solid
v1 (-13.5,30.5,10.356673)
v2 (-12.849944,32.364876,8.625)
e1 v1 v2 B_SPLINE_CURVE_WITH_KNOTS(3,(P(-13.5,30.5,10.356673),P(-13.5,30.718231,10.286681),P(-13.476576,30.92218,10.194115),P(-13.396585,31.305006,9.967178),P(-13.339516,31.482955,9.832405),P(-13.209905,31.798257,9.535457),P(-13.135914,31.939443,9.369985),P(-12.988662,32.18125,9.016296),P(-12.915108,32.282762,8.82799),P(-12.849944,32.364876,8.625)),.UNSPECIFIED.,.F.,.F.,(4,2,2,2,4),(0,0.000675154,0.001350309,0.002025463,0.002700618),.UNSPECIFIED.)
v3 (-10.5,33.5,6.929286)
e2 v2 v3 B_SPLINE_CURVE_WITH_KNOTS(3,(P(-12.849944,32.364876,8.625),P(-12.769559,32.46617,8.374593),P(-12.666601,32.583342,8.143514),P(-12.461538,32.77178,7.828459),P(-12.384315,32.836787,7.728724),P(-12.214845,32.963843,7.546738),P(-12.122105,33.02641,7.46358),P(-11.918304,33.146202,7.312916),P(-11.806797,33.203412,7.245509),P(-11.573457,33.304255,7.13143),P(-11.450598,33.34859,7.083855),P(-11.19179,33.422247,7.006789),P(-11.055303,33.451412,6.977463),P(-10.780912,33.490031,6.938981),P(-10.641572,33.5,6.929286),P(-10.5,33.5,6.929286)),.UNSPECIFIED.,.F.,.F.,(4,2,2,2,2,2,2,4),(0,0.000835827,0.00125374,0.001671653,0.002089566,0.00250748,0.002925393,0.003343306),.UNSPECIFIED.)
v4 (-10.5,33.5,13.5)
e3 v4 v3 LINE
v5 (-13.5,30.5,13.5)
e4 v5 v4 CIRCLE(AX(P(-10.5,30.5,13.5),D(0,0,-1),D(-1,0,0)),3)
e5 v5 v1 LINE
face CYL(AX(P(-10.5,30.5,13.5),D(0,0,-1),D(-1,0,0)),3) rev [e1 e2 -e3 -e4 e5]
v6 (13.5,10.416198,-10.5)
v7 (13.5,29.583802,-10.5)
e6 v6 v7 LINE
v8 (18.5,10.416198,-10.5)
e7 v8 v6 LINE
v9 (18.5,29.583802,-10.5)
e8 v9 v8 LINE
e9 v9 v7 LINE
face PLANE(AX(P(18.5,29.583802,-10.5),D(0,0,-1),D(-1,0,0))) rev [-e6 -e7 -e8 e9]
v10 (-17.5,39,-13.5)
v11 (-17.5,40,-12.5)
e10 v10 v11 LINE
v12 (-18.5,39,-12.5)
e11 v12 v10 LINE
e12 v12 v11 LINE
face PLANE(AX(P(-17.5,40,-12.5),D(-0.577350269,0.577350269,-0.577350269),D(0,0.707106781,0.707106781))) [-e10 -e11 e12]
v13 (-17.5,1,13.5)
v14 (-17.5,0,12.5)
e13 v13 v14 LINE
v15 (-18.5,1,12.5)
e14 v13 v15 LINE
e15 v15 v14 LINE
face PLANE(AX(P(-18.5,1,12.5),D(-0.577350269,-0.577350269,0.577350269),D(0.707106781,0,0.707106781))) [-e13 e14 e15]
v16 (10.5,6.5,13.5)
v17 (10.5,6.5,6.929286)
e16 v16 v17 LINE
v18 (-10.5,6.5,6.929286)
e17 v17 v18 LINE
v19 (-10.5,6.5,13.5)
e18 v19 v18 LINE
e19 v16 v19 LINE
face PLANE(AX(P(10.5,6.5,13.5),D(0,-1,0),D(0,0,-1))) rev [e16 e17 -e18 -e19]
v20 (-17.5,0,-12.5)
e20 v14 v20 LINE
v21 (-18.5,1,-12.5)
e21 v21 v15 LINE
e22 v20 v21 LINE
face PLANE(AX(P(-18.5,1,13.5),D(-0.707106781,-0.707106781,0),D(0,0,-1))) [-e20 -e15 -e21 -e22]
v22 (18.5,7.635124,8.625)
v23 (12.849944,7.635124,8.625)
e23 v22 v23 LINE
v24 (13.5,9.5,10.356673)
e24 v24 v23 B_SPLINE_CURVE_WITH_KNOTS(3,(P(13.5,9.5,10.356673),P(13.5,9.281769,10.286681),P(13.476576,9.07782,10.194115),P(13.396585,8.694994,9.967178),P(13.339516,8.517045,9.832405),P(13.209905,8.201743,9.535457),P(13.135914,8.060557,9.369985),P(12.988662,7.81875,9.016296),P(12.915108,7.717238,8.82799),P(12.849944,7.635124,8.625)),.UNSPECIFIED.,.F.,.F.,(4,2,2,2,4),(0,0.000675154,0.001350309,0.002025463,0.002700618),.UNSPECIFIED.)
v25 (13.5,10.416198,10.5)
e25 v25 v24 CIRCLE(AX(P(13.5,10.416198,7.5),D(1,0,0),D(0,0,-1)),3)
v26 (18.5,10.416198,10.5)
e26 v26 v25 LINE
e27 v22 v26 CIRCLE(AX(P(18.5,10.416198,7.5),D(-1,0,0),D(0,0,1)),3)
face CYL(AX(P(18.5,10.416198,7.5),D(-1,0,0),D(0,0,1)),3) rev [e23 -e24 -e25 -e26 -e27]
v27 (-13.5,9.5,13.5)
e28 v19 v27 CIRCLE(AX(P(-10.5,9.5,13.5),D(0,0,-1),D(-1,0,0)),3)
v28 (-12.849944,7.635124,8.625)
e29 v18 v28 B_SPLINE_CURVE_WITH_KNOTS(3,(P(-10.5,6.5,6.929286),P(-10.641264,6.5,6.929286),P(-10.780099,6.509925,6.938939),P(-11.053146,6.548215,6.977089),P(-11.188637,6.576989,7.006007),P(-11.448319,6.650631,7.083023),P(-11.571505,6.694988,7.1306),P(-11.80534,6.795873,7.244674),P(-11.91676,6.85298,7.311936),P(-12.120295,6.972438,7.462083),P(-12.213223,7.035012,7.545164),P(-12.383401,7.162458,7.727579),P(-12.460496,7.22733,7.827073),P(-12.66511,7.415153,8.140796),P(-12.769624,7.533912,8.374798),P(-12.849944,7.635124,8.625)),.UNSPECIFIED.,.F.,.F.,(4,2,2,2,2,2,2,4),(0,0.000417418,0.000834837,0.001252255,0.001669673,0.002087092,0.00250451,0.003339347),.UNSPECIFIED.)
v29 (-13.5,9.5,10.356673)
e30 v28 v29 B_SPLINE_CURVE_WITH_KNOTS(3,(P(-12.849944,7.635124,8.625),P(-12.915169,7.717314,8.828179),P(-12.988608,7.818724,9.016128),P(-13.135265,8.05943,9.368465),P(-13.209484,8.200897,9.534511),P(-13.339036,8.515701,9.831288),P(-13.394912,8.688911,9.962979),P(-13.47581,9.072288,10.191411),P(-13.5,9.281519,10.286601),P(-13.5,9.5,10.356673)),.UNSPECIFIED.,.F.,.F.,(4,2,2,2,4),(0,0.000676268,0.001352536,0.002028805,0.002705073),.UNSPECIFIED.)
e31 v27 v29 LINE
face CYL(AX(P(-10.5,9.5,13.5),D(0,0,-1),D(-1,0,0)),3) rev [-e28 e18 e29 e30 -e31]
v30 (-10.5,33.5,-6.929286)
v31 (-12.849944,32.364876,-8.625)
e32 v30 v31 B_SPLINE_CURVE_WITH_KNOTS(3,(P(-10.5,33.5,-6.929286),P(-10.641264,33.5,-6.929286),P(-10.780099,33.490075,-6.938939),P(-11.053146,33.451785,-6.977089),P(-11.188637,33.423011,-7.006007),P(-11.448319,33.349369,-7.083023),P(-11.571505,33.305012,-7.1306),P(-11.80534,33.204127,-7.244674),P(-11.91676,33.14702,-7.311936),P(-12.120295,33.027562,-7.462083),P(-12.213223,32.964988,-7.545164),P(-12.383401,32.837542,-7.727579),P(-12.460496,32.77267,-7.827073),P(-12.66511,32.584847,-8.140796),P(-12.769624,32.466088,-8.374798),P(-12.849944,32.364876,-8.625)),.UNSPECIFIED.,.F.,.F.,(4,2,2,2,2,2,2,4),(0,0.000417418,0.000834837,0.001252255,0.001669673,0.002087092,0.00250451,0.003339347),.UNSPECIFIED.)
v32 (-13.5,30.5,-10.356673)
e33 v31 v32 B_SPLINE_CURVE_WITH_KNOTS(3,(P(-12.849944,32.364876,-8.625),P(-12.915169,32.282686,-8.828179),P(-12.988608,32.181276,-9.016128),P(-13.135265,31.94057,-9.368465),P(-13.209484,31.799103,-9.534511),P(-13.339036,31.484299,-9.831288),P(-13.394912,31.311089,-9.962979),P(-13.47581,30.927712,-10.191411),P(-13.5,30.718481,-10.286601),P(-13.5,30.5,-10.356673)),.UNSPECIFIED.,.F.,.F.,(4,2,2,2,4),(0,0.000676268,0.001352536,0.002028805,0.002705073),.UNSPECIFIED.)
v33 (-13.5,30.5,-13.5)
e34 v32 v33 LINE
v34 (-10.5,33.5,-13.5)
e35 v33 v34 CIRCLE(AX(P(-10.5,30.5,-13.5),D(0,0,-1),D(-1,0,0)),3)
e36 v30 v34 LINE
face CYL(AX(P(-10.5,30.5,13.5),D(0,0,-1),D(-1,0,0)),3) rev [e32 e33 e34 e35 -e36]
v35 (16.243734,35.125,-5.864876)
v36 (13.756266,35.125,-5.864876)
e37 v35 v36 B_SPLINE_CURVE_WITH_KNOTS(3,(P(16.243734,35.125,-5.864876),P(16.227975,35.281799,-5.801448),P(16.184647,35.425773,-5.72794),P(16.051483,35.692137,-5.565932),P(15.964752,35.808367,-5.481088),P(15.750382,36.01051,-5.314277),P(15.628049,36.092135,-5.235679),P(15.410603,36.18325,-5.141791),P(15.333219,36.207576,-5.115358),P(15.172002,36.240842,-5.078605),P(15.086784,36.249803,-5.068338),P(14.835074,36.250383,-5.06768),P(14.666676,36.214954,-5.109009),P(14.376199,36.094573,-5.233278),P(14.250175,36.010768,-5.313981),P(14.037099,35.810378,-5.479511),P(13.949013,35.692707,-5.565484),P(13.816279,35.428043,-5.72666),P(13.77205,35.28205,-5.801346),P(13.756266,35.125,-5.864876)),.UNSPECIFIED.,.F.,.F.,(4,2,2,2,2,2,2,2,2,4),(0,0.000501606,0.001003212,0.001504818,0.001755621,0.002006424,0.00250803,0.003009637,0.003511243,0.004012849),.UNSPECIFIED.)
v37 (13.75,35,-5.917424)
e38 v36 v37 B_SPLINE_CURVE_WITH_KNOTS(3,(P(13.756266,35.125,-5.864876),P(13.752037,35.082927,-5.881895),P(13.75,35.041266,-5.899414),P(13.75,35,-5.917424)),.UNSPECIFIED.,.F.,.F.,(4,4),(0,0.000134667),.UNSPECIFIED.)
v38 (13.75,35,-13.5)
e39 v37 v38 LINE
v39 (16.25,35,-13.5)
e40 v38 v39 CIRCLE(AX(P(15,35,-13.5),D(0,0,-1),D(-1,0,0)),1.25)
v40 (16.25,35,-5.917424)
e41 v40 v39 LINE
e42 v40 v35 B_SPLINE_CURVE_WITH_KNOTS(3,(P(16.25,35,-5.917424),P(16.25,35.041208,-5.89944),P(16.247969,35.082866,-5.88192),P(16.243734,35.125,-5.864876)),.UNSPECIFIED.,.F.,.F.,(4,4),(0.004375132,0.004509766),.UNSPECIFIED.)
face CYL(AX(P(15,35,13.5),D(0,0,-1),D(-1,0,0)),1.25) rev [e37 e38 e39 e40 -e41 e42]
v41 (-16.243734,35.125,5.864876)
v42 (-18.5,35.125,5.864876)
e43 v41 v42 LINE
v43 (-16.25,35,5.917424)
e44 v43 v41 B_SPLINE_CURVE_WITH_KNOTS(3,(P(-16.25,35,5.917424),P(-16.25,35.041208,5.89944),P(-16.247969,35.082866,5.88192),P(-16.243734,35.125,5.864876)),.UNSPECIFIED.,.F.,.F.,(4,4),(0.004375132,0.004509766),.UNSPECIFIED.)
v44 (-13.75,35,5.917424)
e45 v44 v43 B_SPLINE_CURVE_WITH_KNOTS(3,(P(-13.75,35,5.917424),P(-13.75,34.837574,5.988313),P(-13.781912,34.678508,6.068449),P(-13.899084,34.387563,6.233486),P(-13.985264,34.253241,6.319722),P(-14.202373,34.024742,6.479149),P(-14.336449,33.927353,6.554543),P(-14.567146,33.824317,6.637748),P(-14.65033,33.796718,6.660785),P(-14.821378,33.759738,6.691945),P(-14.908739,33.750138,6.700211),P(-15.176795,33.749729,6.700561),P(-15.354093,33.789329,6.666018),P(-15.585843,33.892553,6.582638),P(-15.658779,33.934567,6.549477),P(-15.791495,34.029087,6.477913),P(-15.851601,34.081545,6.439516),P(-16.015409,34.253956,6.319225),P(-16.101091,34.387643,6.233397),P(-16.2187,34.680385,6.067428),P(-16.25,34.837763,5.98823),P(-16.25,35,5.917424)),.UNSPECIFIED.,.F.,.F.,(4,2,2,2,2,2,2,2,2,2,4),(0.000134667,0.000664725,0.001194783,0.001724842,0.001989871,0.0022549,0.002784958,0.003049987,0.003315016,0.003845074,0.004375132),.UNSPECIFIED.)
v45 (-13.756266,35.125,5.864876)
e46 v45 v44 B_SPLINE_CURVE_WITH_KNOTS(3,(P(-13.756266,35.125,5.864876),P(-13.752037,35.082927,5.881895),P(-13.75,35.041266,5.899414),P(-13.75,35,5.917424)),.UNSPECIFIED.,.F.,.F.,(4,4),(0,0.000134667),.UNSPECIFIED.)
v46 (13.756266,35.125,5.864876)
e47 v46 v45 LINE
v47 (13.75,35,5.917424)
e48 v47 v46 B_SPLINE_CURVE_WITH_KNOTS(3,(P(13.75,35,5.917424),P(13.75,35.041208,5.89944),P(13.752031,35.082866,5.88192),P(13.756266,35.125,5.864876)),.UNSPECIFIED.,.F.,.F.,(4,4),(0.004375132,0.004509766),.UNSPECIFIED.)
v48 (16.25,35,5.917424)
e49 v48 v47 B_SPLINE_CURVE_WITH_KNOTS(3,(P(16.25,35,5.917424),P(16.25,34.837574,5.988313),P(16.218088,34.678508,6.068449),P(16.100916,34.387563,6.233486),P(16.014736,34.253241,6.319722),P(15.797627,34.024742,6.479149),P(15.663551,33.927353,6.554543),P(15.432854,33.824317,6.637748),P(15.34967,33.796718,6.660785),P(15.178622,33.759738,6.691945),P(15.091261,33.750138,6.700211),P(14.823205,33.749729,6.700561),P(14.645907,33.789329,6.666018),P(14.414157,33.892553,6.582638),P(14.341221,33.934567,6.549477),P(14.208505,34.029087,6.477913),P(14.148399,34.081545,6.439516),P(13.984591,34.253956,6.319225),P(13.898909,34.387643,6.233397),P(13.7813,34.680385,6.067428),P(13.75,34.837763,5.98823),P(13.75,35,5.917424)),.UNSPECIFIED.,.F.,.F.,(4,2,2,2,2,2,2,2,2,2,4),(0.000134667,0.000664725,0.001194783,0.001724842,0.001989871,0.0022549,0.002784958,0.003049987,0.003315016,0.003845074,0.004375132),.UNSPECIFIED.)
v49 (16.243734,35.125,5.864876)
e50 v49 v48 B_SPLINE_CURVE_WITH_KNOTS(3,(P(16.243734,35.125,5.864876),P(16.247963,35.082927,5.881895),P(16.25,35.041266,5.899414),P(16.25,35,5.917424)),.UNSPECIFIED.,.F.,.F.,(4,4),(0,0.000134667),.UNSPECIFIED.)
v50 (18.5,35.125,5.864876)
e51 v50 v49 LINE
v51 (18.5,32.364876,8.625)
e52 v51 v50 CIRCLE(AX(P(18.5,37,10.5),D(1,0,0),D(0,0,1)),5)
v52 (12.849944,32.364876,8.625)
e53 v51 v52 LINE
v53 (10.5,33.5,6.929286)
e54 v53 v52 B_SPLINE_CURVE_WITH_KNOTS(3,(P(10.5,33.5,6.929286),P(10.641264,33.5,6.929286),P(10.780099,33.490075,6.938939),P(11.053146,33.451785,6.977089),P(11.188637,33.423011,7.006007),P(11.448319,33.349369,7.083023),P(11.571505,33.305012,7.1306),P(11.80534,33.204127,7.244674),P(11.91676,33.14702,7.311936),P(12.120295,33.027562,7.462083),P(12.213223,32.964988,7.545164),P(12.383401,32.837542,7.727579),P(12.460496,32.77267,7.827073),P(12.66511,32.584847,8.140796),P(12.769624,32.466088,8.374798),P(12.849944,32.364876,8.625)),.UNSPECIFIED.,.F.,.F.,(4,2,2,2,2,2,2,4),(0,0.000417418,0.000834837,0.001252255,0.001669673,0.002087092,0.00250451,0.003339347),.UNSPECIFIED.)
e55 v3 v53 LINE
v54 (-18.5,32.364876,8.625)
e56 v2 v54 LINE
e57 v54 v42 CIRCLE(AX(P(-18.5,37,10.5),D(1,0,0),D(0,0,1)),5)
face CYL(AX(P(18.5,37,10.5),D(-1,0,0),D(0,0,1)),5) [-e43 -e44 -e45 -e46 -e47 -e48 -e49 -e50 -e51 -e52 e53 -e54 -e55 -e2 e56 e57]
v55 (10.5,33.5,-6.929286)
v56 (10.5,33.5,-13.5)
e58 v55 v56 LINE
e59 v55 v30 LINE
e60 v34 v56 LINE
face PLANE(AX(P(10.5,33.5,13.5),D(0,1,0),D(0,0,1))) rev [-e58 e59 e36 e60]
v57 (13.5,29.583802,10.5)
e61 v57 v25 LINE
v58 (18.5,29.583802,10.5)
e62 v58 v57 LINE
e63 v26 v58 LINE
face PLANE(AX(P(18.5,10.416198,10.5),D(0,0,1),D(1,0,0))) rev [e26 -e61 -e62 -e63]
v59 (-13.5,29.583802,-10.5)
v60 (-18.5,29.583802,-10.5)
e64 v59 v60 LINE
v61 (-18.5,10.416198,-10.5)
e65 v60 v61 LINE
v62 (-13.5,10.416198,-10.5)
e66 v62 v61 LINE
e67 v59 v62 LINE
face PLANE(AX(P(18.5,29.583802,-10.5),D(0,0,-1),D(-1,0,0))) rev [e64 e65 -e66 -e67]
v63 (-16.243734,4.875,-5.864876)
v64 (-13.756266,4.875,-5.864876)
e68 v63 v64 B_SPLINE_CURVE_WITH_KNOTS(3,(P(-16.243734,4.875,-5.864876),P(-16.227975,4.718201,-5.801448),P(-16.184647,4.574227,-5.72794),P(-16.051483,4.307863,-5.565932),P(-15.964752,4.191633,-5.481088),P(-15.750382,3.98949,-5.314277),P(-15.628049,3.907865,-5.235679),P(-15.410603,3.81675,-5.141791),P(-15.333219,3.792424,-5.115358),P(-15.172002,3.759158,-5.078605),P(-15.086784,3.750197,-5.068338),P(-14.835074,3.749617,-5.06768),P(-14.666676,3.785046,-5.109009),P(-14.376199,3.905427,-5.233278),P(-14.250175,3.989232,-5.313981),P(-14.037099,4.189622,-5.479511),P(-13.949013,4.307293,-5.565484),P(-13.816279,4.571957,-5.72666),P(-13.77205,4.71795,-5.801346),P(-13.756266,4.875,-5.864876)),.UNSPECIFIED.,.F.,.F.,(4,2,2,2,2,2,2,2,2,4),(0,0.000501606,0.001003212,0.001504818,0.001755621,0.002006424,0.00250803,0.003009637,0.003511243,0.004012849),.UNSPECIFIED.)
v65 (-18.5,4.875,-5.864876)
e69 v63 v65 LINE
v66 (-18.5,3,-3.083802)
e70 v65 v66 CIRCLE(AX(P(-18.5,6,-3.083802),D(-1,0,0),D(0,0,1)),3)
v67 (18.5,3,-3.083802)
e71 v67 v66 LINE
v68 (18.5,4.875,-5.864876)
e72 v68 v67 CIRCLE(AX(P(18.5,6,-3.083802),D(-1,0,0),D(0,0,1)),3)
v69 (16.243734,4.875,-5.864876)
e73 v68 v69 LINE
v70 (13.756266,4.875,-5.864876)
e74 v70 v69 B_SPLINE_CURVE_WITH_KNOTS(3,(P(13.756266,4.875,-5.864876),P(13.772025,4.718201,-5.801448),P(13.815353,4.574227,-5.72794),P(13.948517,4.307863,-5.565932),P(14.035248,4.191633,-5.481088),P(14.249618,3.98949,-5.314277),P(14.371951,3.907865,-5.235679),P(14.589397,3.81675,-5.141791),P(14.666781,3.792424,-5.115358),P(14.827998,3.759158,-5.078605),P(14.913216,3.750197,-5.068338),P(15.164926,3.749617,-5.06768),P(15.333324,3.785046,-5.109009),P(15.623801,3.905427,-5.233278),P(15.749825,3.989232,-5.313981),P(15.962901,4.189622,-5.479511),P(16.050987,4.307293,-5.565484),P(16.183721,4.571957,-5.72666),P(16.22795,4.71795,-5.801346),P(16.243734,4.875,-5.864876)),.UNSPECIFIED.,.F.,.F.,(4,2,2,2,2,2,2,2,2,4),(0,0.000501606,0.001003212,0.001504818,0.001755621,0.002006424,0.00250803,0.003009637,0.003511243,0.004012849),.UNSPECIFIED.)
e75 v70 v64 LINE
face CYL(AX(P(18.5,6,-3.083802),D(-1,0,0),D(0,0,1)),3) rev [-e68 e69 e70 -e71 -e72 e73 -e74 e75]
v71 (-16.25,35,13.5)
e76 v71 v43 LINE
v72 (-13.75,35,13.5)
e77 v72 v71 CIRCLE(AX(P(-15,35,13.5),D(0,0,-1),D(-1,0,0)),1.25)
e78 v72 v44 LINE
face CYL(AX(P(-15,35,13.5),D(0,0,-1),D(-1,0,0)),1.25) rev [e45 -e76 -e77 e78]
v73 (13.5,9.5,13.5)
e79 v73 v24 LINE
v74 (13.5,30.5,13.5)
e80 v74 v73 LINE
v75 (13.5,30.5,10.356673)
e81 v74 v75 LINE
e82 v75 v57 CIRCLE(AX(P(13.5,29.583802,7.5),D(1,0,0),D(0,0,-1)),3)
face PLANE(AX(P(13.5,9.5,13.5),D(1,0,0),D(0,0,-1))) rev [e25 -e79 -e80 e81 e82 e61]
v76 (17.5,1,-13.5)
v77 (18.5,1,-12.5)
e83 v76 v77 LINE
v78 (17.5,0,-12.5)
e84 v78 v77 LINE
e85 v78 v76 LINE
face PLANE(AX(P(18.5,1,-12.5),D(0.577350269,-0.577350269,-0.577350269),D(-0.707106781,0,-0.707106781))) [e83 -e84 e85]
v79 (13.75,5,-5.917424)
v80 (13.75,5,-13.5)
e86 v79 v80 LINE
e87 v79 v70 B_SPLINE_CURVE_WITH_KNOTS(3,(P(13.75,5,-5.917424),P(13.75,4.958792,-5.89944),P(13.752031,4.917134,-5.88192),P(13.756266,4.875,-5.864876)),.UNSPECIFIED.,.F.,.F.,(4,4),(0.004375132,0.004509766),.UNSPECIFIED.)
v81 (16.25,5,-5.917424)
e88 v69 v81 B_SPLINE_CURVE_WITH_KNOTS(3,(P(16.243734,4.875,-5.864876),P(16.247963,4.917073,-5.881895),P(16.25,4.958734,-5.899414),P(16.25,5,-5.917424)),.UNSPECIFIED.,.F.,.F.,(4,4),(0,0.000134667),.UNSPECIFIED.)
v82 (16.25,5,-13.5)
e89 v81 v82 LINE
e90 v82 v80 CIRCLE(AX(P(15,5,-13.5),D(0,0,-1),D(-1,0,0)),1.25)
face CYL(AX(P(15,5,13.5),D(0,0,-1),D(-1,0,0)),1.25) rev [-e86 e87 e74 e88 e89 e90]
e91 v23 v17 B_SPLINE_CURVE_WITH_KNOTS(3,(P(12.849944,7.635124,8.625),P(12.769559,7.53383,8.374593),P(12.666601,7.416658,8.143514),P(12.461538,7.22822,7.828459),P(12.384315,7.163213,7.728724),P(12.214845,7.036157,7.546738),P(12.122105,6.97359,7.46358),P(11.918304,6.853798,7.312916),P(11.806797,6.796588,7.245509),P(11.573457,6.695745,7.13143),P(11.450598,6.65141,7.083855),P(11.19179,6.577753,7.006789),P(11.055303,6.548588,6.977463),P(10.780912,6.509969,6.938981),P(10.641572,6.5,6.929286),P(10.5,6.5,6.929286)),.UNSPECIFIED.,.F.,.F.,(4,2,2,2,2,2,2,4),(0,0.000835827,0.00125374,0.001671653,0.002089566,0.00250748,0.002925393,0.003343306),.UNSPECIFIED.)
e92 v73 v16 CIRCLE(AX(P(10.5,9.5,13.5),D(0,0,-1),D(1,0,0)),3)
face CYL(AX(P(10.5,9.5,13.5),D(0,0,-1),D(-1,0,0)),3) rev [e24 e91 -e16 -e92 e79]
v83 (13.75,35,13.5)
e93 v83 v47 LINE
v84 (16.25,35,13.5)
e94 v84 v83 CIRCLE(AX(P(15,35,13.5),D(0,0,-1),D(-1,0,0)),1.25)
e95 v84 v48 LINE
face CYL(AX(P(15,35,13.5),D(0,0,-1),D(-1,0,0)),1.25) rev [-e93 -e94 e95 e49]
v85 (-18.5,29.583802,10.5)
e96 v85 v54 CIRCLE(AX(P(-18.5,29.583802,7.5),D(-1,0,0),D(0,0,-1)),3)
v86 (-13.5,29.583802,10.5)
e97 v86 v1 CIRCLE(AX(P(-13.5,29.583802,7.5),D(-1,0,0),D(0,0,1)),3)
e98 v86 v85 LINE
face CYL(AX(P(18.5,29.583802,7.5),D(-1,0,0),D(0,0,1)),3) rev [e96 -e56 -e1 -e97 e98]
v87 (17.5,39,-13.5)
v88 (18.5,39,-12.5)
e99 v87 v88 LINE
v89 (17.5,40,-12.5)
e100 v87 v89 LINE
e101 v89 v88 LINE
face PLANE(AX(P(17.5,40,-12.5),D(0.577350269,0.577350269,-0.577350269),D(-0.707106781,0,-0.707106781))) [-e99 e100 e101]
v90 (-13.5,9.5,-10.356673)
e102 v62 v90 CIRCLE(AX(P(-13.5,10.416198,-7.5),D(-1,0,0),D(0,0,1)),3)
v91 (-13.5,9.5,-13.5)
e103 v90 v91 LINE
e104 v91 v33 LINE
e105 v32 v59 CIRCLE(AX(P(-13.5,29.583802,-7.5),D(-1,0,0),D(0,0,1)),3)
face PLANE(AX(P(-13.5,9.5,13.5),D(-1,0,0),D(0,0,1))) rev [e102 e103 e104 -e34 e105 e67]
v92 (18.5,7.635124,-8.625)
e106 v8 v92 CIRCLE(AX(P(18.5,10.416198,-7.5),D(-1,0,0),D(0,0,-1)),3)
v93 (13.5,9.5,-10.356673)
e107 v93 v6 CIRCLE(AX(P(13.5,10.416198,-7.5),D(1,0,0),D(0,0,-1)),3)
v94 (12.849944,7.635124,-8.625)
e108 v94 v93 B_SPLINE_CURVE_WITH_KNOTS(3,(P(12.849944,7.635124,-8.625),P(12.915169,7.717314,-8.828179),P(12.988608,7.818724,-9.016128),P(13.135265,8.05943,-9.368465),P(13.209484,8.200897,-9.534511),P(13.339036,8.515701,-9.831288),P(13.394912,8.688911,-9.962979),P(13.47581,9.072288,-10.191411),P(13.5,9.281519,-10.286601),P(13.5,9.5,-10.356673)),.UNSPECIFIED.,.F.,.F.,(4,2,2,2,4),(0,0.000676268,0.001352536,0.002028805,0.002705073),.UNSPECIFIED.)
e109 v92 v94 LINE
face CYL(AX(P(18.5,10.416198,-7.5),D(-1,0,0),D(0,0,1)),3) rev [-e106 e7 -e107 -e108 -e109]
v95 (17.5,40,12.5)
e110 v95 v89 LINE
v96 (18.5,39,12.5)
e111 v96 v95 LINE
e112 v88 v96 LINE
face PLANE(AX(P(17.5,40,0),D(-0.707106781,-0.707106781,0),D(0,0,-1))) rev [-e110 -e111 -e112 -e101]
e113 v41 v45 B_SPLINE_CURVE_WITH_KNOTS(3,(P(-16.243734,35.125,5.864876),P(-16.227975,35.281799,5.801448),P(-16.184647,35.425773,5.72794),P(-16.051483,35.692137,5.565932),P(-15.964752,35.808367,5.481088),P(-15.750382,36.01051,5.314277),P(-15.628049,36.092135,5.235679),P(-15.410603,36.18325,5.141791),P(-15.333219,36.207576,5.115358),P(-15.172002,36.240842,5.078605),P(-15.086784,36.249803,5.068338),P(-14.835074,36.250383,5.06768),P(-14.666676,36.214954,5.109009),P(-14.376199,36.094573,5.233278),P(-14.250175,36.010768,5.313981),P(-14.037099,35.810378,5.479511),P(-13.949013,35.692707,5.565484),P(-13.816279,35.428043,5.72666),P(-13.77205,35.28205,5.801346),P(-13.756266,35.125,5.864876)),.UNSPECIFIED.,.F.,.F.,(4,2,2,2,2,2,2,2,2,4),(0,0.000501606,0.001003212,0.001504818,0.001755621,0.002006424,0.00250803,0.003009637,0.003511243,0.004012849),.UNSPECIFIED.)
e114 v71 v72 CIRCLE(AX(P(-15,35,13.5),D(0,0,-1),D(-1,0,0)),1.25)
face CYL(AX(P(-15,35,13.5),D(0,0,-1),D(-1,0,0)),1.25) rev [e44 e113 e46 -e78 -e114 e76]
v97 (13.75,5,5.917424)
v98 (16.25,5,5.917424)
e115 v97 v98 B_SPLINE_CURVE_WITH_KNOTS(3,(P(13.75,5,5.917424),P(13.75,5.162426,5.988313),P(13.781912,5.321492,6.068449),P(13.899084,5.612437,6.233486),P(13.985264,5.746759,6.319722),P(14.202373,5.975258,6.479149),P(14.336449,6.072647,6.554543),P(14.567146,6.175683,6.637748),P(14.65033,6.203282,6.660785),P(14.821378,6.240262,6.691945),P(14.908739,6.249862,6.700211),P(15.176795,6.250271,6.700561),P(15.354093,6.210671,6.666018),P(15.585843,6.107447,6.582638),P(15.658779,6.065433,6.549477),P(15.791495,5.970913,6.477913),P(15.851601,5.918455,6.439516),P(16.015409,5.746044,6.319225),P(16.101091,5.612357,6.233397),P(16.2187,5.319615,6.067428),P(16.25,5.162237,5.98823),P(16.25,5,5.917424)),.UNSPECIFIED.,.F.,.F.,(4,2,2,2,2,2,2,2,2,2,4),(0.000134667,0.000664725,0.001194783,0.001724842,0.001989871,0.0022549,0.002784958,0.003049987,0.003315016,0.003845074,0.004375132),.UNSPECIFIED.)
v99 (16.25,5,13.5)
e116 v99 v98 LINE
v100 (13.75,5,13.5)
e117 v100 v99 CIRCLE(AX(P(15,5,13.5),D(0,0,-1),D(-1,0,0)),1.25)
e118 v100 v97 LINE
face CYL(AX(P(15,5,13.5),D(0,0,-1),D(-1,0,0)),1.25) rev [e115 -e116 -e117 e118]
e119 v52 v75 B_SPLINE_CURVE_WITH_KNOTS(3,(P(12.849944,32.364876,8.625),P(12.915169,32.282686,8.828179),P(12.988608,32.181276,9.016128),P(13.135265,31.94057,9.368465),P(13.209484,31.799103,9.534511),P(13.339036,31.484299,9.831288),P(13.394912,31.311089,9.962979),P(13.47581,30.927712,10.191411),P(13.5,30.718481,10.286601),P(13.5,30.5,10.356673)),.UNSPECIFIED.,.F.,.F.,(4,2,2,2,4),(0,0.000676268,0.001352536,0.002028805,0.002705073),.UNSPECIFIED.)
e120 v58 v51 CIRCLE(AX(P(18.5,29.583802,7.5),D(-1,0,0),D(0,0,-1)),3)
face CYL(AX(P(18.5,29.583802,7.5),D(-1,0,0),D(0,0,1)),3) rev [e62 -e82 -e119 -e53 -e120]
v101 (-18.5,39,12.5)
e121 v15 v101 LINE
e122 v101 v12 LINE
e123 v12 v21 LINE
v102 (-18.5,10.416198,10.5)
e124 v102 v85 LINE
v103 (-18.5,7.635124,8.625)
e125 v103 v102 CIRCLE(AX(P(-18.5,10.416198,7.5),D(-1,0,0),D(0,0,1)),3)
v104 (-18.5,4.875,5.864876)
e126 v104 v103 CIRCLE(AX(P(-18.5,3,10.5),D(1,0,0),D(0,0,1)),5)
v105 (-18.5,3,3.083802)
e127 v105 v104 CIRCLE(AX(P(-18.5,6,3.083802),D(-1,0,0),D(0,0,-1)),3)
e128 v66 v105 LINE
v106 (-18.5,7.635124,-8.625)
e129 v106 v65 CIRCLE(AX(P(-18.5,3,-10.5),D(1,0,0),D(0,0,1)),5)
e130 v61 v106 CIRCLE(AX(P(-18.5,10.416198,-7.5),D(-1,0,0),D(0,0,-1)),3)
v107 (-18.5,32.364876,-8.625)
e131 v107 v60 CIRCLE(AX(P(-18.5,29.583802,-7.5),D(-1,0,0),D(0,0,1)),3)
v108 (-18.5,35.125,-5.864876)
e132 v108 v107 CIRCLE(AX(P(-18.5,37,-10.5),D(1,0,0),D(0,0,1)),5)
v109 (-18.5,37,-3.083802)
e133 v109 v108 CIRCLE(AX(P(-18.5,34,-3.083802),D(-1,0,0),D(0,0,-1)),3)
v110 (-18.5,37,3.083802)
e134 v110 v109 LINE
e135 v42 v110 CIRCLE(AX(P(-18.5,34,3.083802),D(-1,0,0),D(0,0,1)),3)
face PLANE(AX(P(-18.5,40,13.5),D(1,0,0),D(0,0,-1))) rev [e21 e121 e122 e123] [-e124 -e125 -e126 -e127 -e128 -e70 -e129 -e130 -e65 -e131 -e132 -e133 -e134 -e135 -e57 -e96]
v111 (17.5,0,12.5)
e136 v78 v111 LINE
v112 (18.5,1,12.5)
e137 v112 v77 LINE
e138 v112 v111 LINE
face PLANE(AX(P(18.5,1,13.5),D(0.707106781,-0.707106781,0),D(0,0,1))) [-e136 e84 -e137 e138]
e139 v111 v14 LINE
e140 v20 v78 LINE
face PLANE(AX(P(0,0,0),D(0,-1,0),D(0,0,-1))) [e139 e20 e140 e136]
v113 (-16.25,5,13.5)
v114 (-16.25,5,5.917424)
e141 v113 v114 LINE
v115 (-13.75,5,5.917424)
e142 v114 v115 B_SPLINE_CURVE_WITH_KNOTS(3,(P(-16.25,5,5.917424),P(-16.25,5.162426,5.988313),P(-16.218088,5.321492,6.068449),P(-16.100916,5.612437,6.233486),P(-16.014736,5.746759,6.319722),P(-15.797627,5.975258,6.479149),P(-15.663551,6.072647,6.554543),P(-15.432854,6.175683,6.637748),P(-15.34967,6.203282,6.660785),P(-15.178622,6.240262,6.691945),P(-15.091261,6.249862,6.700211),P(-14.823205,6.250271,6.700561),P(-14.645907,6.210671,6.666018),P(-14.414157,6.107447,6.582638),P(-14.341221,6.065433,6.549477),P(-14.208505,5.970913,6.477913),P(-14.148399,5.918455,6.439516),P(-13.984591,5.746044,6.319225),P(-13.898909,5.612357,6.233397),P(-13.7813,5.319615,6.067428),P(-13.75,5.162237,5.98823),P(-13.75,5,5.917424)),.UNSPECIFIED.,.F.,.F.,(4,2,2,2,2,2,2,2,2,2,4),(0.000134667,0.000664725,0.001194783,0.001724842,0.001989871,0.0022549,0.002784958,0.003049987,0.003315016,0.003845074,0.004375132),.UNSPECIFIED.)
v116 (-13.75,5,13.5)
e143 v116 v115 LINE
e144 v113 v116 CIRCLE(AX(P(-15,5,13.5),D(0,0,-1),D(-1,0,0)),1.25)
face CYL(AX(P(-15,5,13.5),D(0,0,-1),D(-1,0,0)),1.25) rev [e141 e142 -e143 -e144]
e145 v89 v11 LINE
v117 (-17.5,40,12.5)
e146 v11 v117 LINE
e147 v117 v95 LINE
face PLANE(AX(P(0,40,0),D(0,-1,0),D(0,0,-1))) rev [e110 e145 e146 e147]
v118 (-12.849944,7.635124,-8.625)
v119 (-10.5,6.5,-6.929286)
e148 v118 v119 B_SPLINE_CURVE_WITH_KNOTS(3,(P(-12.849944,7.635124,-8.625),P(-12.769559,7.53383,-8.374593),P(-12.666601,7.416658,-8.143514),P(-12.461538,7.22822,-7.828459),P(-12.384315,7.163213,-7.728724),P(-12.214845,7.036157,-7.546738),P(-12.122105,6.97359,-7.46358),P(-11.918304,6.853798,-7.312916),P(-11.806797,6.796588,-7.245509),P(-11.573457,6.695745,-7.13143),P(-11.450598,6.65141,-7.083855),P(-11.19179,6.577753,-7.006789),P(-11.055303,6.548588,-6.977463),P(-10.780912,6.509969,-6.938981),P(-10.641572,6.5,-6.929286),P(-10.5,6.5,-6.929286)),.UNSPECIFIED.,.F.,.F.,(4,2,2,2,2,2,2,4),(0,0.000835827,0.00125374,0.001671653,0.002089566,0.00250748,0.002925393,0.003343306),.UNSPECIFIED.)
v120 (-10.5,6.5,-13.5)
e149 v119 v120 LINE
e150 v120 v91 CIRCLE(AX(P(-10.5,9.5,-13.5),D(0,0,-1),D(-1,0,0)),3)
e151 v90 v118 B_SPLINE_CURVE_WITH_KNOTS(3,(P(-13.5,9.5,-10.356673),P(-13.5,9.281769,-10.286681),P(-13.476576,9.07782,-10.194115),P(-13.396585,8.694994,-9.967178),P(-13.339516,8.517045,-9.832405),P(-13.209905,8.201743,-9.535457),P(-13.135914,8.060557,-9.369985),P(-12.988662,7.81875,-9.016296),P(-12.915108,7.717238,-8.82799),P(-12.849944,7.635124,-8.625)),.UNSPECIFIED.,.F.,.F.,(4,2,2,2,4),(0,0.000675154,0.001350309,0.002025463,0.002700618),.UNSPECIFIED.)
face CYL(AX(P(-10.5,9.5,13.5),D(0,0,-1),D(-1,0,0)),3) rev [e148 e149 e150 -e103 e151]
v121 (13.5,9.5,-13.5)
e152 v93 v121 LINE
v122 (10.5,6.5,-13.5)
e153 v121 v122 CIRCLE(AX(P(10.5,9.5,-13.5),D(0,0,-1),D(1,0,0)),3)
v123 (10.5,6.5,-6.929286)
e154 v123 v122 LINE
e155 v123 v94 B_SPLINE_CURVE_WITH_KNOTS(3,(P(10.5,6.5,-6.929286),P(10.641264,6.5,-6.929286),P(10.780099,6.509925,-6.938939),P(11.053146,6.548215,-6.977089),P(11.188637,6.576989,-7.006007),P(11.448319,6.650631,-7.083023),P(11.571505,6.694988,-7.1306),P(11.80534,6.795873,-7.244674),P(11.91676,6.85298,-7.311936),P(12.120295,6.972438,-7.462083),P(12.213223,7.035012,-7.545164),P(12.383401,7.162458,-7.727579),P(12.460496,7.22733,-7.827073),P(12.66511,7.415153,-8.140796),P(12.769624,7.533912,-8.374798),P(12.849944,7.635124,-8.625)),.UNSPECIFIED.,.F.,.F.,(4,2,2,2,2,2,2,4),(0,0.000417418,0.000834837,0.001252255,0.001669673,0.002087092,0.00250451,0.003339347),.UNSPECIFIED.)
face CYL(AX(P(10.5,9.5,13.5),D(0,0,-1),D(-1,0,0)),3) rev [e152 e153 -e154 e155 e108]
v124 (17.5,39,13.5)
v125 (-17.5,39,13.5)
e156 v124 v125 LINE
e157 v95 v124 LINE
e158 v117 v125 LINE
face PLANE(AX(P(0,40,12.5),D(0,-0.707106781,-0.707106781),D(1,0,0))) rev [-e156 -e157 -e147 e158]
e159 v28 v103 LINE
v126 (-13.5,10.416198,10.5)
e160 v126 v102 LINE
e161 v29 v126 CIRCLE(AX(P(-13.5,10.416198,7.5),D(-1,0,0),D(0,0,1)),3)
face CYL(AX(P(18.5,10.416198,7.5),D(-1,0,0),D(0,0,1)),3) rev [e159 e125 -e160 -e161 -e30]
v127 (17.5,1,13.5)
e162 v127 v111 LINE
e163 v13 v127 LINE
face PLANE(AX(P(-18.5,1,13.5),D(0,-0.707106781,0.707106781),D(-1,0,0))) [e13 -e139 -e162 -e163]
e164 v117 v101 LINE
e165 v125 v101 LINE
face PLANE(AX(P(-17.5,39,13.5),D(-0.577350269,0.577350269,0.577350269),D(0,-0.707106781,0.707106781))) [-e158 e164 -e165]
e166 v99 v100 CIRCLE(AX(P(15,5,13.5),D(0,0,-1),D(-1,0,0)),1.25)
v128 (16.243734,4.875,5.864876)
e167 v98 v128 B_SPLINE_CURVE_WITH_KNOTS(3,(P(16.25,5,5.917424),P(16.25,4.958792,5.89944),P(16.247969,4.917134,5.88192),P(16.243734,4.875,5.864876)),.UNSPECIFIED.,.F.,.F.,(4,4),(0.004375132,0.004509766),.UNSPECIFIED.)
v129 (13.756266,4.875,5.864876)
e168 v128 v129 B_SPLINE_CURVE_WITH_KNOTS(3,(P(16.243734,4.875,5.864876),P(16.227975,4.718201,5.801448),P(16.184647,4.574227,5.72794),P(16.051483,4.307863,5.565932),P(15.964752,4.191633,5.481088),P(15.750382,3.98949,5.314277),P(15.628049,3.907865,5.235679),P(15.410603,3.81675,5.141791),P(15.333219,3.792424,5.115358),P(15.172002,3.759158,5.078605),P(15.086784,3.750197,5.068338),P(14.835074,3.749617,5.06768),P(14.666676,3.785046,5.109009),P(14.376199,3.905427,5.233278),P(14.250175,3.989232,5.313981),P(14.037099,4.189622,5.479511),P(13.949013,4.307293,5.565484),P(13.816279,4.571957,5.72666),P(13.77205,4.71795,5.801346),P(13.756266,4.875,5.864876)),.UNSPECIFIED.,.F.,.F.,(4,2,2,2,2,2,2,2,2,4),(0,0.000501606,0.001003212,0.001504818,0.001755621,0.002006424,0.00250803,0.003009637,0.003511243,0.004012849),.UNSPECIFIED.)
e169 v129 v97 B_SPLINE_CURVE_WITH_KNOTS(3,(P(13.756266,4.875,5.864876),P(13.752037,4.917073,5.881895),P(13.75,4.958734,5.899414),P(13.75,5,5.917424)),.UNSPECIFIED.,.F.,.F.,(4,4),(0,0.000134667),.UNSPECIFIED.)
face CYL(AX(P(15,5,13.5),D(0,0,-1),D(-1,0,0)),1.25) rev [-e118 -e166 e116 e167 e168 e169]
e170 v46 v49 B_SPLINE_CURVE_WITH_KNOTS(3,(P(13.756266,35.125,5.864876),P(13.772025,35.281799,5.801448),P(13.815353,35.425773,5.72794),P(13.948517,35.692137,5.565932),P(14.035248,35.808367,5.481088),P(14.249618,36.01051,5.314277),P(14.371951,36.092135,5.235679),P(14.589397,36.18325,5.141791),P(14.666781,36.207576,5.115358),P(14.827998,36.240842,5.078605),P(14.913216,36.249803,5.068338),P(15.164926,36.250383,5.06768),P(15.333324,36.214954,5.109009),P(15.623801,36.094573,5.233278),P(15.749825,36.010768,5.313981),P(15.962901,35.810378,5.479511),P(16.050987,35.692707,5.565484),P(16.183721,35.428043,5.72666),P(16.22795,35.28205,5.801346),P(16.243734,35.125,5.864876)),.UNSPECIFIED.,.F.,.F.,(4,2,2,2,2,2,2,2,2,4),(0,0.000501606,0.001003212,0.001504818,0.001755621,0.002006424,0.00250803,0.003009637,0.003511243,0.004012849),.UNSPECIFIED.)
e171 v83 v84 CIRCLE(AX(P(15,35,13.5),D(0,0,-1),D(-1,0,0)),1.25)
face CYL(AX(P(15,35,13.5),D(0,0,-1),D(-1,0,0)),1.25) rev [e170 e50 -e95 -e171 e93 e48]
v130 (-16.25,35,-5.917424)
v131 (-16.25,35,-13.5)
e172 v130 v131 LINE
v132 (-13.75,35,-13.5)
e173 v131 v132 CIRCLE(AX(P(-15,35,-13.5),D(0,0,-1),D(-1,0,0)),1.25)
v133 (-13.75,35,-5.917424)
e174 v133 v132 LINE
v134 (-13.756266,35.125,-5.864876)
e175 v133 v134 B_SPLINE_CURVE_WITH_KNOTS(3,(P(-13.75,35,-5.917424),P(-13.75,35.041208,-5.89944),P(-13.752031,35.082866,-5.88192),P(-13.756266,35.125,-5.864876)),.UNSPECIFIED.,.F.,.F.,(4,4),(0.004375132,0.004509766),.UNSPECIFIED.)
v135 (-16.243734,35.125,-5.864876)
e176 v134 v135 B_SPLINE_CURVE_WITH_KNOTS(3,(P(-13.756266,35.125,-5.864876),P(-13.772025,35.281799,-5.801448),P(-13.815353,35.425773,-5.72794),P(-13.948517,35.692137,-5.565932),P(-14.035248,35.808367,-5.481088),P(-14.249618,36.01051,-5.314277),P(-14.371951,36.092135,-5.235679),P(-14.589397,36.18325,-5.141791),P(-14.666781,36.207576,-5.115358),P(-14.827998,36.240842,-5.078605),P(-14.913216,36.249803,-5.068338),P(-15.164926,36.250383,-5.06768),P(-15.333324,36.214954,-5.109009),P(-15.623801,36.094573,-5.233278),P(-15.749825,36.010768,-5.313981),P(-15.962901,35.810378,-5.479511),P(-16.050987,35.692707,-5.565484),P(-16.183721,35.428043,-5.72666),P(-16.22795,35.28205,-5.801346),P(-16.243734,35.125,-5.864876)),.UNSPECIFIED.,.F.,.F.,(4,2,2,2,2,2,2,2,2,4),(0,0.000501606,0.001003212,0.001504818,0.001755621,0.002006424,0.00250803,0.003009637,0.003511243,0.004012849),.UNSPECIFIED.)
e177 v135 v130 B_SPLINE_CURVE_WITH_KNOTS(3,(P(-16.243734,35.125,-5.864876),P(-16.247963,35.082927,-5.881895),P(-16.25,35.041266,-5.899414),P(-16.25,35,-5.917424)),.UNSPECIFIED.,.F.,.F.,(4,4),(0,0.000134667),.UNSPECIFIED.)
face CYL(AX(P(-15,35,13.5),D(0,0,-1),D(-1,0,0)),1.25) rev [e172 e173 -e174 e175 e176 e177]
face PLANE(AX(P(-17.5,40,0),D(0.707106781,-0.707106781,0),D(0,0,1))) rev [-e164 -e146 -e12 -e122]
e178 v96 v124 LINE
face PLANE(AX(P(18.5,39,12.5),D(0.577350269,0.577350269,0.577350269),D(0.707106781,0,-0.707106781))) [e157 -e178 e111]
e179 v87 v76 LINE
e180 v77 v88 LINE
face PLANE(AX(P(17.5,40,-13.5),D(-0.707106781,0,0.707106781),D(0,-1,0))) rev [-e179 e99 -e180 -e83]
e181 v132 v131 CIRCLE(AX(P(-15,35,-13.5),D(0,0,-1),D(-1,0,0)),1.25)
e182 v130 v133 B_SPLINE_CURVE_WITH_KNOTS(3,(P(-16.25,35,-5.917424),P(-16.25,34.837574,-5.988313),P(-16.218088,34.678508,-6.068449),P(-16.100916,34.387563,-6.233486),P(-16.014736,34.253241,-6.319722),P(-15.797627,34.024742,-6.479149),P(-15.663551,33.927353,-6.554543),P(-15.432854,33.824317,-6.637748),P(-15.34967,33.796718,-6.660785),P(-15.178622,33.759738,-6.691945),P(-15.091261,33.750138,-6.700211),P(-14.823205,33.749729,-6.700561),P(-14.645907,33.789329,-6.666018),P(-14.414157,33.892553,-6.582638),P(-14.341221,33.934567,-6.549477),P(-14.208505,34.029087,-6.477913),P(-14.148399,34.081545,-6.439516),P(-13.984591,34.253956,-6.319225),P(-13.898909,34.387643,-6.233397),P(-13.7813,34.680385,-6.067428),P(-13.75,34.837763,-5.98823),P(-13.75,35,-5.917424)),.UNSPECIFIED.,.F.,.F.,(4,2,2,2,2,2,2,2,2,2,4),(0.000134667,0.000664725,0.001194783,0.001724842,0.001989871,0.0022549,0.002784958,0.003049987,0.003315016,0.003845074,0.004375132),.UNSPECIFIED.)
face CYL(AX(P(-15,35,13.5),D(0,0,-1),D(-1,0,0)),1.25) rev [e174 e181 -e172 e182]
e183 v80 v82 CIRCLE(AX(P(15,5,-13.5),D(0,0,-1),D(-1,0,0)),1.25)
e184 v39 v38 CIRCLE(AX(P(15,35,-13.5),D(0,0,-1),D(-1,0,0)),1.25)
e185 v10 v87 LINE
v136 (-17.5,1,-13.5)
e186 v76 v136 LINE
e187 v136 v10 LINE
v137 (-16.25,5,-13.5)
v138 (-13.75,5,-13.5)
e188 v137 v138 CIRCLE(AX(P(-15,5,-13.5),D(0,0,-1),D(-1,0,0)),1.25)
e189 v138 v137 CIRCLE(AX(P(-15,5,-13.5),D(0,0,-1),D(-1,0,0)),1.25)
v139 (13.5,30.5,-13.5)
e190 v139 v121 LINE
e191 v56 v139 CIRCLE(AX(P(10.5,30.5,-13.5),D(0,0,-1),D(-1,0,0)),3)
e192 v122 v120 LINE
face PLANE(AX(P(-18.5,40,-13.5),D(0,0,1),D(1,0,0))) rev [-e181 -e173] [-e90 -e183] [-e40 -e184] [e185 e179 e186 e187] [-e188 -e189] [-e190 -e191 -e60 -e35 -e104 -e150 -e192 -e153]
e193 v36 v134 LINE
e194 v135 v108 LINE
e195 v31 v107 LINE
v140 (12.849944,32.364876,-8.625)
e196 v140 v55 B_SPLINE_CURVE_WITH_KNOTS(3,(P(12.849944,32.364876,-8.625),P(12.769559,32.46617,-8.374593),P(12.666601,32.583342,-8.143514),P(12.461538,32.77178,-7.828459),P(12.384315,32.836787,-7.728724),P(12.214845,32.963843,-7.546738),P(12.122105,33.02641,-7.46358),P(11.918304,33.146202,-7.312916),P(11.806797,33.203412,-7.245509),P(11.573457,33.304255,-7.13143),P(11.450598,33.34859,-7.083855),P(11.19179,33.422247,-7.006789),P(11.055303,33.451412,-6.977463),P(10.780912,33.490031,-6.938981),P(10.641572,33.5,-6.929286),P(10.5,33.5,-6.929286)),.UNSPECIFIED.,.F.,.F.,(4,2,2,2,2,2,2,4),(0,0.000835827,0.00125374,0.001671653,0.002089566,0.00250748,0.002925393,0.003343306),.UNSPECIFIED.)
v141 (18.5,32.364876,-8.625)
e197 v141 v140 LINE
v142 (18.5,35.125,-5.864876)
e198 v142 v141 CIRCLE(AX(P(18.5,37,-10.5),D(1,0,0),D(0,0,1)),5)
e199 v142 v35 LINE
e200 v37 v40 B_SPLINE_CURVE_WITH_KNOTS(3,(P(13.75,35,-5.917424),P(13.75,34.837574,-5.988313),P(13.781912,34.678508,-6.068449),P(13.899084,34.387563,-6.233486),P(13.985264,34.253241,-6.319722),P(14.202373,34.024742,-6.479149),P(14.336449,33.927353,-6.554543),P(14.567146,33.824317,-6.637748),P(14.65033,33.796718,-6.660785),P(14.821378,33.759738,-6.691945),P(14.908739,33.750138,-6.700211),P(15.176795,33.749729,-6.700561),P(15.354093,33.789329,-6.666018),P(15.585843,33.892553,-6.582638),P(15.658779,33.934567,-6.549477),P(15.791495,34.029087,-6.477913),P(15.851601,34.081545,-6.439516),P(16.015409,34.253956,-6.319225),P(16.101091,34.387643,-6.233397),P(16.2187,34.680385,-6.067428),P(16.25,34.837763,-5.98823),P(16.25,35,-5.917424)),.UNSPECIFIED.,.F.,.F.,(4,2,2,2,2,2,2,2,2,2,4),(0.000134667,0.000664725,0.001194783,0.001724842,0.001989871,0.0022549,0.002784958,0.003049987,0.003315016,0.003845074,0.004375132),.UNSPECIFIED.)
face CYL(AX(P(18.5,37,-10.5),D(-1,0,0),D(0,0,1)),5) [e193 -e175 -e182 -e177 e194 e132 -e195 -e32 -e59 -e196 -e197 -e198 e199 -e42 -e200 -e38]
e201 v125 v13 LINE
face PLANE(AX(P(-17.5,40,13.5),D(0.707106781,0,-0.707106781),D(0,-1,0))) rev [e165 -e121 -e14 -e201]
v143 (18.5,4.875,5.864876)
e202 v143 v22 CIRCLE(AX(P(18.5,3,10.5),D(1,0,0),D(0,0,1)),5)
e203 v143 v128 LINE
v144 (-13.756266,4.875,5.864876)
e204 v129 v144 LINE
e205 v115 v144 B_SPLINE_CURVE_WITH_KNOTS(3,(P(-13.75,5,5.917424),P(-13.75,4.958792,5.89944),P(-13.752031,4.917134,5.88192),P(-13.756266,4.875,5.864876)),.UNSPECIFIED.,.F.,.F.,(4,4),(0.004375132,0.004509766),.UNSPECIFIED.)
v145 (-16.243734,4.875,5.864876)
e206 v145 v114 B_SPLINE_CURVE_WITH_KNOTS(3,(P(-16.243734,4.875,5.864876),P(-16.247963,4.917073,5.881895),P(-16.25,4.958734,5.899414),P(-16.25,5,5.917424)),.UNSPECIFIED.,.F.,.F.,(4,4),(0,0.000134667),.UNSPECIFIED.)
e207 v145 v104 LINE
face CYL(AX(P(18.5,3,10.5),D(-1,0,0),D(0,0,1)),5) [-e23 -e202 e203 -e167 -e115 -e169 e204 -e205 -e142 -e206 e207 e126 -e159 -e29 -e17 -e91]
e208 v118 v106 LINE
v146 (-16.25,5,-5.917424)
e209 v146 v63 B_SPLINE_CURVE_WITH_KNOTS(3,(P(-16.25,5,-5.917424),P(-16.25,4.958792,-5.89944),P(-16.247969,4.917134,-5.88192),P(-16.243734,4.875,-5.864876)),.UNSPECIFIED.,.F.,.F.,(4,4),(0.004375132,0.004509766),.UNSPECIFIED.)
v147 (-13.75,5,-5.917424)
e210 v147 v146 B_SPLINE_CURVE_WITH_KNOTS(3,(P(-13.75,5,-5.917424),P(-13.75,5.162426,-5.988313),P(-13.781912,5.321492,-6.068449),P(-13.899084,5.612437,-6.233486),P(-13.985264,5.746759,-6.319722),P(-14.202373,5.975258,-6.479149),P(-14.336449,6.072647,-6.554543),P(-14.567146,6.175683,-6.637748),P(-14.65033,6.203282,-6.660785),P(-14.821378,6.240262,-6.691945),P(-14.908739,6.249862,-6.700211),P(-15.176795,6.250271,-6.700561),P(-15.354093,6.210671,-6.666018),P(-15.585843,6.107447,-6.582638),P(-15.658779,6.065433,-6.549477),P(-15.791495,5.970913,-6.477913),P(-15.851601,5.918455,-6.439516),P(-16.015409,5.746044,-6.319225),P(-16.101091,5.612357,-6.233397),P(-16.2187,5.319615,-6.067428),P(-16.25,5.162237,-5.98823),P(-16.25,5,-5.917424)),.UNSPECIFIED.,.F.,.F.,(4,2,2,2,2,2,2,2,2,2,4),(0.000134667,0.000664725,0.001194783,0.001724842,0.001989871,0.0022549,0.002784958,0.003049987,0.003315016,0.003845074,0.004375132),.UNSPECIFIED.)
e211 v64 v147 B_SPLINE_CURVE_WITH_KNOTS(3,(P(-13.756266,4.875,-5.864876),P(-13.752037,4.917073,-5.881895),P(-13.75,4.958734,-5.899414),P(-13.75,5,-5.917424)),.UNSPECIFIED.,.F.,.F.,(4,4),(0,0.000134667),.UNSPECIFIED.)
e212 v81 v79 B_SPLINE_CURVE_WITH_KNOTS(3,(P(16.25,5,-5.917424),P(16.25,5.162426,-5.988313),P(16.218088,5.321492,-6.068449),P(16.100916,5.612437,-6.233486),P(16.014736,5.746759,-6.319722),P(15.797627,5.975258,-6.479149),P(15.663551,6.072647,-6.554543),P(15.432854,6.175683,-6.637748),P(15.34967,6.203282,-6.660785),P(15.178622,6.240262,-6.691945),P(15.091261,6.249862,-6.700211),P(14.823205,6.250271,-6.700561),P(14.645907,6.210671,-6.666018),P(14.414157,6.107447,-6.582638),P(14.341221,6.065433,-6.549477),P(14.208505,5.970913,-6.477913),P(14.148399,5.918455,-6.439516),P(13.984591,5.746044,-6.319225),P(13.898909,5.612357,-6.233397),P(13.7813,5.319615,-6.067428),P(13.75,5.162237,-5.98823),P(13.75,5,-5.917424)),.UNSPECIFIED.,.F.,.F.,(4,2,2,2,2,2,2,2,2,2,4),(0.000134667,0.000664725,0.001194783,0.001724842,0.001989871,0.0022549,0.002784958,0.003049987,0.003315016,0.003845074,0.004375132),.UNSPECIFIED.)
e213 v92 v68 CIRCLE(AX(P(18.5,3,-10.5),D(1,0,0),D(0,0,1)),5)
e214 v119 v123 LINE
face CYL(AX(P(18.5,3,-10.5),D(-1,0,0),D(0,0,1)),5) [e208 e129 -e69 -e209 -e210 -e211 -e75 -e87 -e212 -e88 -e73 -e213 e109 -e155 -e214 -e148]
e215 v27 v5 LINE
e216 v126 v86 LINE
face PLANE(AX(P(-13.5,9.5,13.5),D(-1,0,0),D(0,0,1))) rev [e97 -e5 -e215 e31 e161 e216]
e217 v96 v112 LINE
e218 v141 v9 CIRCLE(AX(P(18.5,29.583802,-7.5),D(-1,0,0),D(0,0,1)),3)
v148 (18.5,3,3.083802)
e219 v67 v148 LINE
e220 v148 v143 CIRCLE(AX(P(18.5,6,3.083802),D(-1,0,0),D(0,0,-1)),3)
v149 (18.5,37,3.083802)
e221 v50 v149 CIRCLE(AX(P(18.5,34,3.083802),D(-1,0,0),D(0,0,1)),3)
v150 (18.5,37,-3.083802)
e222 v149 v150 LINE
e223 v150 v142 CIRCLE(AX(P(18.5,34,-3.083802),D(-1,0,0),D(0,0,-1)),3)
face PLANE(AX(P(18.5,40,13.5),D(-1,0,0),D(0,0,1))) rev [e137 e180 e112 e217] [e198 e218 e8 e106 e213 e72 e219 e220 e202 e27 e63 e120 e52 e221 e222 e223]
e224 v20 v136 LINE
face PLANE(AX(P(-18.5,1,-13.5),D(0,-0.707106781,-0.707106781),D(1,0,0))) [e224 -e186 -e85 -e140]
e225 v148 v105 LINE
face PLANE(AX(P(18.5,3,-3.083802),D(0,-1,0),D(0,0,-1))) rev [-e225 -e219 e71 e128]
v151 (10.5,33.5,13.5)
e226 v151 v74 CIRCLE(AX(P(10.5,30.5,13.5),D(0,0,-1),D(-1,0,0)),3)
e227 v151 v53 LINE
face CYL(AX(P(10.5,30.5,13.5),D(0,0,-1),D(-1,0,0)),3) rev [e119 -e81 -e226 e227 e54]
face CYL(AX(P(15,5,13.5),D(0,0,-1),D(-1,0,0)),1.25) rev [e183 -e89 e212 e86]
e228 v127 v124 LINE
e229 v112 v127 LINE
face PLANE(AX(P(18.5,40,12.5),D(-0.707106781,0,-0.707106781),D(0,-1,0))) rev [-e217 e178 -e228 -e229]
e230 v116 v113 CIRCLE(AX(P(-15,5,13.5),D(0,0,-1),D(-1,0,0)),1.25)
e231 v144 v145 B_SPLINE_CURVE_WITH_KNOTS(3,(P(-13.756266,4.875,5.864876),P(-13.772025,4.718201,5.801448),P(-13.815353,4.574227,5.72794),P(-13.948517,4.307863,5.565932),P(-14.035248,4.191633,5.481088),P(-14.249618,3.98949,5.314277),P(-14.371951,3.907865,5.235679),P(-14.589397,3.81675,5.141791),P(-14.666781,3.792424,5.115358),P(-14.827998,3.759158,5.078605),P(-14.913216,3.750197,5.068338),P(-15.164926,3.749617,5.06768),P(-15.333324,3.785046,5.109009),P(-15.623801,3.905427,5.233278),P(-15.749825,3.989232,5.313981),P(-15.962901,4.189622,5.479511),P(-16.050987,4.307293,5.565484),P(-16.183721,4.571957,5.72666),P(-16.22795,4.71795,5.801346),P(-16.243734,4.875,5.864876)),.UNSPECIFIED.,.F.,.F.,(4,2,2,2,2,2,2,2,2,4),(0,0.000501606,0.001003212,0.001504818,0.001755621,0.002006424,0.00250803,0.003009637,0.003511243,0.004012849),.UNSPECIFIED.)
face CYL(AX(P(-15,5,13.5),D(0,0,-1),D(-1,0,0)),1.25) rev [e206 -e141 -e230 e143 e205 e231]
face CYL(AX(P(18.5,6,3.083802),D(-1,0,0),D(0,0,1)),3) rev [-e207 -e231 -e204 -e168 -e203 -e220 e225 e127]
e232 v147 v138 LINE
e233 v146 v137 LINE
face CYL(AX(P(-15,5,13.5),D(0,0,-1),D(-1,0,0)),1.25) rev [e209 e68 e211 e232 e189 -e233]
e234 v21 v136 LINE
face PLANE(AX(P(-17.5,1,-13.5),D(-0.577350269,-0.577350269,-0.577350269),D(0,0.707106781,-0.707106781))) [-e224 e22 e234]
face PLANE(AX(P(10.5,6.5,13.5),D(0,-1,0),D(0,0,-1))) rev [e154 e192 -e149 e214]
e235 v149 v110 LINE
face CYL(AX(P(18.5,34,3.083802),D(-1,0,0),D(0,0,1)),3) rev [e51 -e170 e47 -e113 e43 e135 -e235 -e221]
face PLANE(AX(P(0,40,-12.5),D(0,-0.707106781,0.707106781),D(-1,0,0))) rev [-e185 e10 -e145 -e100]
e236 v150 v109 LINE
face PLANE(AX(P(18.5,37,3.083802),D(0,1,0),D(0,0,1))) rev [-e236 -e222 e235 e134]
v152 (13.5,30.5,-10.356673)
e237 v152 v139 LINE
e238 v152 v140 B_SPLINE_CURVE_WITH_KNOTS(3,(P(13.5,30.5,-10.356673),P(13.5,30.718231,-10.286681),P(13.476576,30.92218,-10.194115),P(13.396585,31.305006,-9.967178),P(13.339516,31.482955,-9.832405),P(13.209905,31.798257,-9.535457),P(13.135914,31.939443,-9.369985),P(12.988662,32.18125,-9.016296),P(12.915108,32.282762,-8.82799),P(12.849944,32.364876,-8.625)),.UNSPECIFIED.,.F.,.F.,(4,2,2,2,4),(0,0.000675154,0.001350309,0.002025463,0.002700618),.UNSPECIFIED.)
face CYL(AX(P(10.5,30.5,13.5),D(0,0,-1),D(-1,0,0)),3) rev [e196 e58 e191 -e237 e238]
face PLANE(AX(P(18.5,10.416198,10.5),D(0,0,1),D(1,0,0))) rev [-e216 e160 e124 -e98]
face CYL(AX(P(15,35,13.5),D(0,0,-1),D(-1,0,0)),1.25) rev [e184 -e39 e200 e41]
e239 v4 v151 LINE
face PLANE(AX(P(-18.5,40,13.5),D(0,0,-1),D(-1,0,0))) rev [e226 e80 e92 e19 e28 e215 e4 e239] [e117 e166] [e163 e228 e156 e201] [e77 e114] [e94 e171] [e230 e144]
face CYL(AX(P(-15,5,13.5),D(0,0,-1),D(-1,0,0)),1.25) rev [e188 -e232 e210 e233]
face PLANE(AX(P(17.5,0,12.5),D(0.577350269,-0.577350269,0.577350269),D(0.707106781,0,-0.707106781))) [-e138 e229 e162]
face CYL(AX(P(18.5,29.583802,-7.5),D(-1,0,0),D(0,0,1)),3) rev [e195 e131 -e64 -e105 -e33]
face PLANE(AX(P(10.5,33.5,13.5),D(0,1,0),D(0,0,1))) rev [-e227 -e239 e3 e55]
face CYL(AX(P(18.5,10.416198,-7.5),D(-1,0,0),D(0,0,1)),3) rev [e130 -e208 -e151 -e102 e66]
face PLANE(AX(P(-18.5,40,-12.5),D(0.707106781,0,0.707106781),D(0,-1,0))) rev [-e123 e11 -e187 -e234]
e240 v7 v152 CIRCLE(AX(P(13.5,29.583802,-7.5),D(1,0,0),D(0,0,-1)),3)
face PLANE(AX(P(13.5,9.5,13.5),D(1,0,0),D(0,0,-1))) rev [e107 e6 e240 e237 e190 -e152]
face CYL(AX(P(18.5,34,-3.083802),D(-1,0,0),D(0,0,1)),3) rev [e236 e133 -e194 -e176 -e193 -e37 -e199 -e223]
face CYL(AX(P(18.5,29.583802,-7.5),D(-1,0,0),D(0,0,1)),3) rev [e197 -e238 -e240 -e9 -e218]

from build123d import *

# Parameters (mm, degrees)
SKETCH_1_W          = 37
SKETCH_1_H          = 27
EXTRUDE_1_DEPTH     = 40
SKETCH_3_R          = 1.25
CUT_EXTRUDE_3_DEPTH = 52.684136831
HOLE_WIZARD_M3_1_D  = 2.5
CUT_EXTRUDE_4_DEPTH = 57.135995582
CHAMFER_1_SIZE      = 1


with BuildPart() as part:
    # 草图1 → 凸台-拉伸1 (new body)
    with BuildSketch(Plane(origin=(0, 0, 0), x_dir=(1, 0, 0), z_dir=(0, 1, 0))):
        Rectangle(SKETCH_1_W, SKETCH_1_H)
    extrude(amount=EXTRUDE_1_DEPTH)

    # 草图3 → 切除-拉伸3 (cut, through all)
    with BuildSketch(Plane(origin=(0, 0, -13.5), x_dir=(-1, 0, 0), z_dir=(0, 0, -1))):
        with Locations((-15, 35)):
            Circle(SKETCH_3_R)
        with Locations((15, 35)):
            Circle(SKETCH_3_R)
        with Locations((-15, 5)):
            Circle(SKETCH_3_R)
        with Locations((15, 5)):
            Circle(SKETCH_3_R)
        with BuildLine():
            Line((-10.5, 6.5), (10.5, 6.5))
            ThreePointArc((10.5, 6.5), (12.621320344, 7.378679656), (13.5, 9.5))
            Line((13.5, 9.5), (13.5, 30.5))
            ThreePointArc((13.5, 30.5), (12.621320344, 32.621320344), (10.5, 33.5))
            Line((10.5, 33.5), (-10.5, 33.5))
            ThreePointArc((-10.5, 33.5), (-12.621320344, 32.621320344), (-13.5, 30.5))
            Line((-13.5, 30.5), (-13.5, 9.5))
            ThreePointArc((-13.5, 9.5), (-12.621320344, 7.378679656), (-10.5, 6.5))
        make_face()
    extrude(amount=-CUT_EXTRUDE_3_DEPTH, mode=Mode.SUBTRACT)

    # M3 螺纹孔1 (through all)
    with Locations(Plane(origin=(-15, 5, -13.5), x_dir=(-1, 0, 0), z_dir=(0, 0, -1))):
        with Locations((0, 0), (0, 30), (-30, 30), (-30, 0)):
            Hole(HOLE_WIZARD_M3_1_D / 2)

    # 草图7 → 切除-拉伸4 (cut, through all)
    with BuildSketch(Plane.ZY.offset(18.5)):
        with BuildLine():
            Line((-3.083801513, 3), (3.083801513, 3))
            ThreePointArc((3.083801513, 3), (4.760852496, 3.512531407), (5.864875946, 4.875))
            ThreePointArc((5.864875946, 4.875), (6.964466094, 6.535533906), (8.625, 7.635124054))
            ThreePointArc((8.625, 7.635124054), (9.987468593, 8.739147504), (10.5, 10.416198487))
            Line((10.5, 10.416198487), (10.5, 29.583801513))
            ThreePointArc((10.5, 29.583801513), (9.987468593, 31.260852496), (8.625, 32.364875946))
            ThreePointArc((8.625, 32.364875946), (6.964466094, 33.464466094), (5.864875946, 35.125))
            ThreePointArc((5.864875946, 35.125), (4.760852496, 36.487468593), (3.083801513, 37))
            Line((3.083801513, 37), (-3.083801513, 37))
            ThreePointArc((-3.083801513, 37), (-4.760852496, 36.487468593), (-5.864875946, 35.125))
            ThreePointArc((-5.864875946, 35.125), (-6.964466094, 33.464466094), (-8.625, 32.364875946))
            ThreePointArc((-8.625, 32.364875946), (-9.987468593, 31.260852496), (-10.5, 29.583801513))
            Line((-10.5, 29.583801513), (-10.5, 10.416198487))
            ThreePointArc((-10.5, 10.416198487), (-9.987468593, 8.739147504), (-8.625, 7.635124054))
            ThreePointArc((-8.625, 7.635124054), (-6.964466094, 6.535533906), (-5.864875946, 4.875))
            ThreePointArc((-5.864875946, 4.875), (-4.760852496, 3.512531407), (-3.083801513, 3))
        make_face()
    extrude(amount=-CUT_EXTRUDE_4_DEPTH, mode=Mode.SUBTRACT)

    # 倒角1
    chamfer_1_edges = [part.edges().sort_by_distance(p)[0] for p in [
        (-18.5, 40, 0),
        (0, 40, 13.5),
        (18.5, 40, 0),
        (0, 0, 13.5),
        (-18.5, 0, 0),
        (0, 0, -13.5),
        (18.5, 0, 0),
        (18.5, 20, 13.5),
        (-18.5, 20, 13.5),
        (-18.5, 20, -13.5),
        (18.5, 20, -13.5),
        (0, 40, -13.5),
    ]]
    chamfer(chamfer_1_edges, length=CHAMFER_1_SIZE)


solid = part.part
